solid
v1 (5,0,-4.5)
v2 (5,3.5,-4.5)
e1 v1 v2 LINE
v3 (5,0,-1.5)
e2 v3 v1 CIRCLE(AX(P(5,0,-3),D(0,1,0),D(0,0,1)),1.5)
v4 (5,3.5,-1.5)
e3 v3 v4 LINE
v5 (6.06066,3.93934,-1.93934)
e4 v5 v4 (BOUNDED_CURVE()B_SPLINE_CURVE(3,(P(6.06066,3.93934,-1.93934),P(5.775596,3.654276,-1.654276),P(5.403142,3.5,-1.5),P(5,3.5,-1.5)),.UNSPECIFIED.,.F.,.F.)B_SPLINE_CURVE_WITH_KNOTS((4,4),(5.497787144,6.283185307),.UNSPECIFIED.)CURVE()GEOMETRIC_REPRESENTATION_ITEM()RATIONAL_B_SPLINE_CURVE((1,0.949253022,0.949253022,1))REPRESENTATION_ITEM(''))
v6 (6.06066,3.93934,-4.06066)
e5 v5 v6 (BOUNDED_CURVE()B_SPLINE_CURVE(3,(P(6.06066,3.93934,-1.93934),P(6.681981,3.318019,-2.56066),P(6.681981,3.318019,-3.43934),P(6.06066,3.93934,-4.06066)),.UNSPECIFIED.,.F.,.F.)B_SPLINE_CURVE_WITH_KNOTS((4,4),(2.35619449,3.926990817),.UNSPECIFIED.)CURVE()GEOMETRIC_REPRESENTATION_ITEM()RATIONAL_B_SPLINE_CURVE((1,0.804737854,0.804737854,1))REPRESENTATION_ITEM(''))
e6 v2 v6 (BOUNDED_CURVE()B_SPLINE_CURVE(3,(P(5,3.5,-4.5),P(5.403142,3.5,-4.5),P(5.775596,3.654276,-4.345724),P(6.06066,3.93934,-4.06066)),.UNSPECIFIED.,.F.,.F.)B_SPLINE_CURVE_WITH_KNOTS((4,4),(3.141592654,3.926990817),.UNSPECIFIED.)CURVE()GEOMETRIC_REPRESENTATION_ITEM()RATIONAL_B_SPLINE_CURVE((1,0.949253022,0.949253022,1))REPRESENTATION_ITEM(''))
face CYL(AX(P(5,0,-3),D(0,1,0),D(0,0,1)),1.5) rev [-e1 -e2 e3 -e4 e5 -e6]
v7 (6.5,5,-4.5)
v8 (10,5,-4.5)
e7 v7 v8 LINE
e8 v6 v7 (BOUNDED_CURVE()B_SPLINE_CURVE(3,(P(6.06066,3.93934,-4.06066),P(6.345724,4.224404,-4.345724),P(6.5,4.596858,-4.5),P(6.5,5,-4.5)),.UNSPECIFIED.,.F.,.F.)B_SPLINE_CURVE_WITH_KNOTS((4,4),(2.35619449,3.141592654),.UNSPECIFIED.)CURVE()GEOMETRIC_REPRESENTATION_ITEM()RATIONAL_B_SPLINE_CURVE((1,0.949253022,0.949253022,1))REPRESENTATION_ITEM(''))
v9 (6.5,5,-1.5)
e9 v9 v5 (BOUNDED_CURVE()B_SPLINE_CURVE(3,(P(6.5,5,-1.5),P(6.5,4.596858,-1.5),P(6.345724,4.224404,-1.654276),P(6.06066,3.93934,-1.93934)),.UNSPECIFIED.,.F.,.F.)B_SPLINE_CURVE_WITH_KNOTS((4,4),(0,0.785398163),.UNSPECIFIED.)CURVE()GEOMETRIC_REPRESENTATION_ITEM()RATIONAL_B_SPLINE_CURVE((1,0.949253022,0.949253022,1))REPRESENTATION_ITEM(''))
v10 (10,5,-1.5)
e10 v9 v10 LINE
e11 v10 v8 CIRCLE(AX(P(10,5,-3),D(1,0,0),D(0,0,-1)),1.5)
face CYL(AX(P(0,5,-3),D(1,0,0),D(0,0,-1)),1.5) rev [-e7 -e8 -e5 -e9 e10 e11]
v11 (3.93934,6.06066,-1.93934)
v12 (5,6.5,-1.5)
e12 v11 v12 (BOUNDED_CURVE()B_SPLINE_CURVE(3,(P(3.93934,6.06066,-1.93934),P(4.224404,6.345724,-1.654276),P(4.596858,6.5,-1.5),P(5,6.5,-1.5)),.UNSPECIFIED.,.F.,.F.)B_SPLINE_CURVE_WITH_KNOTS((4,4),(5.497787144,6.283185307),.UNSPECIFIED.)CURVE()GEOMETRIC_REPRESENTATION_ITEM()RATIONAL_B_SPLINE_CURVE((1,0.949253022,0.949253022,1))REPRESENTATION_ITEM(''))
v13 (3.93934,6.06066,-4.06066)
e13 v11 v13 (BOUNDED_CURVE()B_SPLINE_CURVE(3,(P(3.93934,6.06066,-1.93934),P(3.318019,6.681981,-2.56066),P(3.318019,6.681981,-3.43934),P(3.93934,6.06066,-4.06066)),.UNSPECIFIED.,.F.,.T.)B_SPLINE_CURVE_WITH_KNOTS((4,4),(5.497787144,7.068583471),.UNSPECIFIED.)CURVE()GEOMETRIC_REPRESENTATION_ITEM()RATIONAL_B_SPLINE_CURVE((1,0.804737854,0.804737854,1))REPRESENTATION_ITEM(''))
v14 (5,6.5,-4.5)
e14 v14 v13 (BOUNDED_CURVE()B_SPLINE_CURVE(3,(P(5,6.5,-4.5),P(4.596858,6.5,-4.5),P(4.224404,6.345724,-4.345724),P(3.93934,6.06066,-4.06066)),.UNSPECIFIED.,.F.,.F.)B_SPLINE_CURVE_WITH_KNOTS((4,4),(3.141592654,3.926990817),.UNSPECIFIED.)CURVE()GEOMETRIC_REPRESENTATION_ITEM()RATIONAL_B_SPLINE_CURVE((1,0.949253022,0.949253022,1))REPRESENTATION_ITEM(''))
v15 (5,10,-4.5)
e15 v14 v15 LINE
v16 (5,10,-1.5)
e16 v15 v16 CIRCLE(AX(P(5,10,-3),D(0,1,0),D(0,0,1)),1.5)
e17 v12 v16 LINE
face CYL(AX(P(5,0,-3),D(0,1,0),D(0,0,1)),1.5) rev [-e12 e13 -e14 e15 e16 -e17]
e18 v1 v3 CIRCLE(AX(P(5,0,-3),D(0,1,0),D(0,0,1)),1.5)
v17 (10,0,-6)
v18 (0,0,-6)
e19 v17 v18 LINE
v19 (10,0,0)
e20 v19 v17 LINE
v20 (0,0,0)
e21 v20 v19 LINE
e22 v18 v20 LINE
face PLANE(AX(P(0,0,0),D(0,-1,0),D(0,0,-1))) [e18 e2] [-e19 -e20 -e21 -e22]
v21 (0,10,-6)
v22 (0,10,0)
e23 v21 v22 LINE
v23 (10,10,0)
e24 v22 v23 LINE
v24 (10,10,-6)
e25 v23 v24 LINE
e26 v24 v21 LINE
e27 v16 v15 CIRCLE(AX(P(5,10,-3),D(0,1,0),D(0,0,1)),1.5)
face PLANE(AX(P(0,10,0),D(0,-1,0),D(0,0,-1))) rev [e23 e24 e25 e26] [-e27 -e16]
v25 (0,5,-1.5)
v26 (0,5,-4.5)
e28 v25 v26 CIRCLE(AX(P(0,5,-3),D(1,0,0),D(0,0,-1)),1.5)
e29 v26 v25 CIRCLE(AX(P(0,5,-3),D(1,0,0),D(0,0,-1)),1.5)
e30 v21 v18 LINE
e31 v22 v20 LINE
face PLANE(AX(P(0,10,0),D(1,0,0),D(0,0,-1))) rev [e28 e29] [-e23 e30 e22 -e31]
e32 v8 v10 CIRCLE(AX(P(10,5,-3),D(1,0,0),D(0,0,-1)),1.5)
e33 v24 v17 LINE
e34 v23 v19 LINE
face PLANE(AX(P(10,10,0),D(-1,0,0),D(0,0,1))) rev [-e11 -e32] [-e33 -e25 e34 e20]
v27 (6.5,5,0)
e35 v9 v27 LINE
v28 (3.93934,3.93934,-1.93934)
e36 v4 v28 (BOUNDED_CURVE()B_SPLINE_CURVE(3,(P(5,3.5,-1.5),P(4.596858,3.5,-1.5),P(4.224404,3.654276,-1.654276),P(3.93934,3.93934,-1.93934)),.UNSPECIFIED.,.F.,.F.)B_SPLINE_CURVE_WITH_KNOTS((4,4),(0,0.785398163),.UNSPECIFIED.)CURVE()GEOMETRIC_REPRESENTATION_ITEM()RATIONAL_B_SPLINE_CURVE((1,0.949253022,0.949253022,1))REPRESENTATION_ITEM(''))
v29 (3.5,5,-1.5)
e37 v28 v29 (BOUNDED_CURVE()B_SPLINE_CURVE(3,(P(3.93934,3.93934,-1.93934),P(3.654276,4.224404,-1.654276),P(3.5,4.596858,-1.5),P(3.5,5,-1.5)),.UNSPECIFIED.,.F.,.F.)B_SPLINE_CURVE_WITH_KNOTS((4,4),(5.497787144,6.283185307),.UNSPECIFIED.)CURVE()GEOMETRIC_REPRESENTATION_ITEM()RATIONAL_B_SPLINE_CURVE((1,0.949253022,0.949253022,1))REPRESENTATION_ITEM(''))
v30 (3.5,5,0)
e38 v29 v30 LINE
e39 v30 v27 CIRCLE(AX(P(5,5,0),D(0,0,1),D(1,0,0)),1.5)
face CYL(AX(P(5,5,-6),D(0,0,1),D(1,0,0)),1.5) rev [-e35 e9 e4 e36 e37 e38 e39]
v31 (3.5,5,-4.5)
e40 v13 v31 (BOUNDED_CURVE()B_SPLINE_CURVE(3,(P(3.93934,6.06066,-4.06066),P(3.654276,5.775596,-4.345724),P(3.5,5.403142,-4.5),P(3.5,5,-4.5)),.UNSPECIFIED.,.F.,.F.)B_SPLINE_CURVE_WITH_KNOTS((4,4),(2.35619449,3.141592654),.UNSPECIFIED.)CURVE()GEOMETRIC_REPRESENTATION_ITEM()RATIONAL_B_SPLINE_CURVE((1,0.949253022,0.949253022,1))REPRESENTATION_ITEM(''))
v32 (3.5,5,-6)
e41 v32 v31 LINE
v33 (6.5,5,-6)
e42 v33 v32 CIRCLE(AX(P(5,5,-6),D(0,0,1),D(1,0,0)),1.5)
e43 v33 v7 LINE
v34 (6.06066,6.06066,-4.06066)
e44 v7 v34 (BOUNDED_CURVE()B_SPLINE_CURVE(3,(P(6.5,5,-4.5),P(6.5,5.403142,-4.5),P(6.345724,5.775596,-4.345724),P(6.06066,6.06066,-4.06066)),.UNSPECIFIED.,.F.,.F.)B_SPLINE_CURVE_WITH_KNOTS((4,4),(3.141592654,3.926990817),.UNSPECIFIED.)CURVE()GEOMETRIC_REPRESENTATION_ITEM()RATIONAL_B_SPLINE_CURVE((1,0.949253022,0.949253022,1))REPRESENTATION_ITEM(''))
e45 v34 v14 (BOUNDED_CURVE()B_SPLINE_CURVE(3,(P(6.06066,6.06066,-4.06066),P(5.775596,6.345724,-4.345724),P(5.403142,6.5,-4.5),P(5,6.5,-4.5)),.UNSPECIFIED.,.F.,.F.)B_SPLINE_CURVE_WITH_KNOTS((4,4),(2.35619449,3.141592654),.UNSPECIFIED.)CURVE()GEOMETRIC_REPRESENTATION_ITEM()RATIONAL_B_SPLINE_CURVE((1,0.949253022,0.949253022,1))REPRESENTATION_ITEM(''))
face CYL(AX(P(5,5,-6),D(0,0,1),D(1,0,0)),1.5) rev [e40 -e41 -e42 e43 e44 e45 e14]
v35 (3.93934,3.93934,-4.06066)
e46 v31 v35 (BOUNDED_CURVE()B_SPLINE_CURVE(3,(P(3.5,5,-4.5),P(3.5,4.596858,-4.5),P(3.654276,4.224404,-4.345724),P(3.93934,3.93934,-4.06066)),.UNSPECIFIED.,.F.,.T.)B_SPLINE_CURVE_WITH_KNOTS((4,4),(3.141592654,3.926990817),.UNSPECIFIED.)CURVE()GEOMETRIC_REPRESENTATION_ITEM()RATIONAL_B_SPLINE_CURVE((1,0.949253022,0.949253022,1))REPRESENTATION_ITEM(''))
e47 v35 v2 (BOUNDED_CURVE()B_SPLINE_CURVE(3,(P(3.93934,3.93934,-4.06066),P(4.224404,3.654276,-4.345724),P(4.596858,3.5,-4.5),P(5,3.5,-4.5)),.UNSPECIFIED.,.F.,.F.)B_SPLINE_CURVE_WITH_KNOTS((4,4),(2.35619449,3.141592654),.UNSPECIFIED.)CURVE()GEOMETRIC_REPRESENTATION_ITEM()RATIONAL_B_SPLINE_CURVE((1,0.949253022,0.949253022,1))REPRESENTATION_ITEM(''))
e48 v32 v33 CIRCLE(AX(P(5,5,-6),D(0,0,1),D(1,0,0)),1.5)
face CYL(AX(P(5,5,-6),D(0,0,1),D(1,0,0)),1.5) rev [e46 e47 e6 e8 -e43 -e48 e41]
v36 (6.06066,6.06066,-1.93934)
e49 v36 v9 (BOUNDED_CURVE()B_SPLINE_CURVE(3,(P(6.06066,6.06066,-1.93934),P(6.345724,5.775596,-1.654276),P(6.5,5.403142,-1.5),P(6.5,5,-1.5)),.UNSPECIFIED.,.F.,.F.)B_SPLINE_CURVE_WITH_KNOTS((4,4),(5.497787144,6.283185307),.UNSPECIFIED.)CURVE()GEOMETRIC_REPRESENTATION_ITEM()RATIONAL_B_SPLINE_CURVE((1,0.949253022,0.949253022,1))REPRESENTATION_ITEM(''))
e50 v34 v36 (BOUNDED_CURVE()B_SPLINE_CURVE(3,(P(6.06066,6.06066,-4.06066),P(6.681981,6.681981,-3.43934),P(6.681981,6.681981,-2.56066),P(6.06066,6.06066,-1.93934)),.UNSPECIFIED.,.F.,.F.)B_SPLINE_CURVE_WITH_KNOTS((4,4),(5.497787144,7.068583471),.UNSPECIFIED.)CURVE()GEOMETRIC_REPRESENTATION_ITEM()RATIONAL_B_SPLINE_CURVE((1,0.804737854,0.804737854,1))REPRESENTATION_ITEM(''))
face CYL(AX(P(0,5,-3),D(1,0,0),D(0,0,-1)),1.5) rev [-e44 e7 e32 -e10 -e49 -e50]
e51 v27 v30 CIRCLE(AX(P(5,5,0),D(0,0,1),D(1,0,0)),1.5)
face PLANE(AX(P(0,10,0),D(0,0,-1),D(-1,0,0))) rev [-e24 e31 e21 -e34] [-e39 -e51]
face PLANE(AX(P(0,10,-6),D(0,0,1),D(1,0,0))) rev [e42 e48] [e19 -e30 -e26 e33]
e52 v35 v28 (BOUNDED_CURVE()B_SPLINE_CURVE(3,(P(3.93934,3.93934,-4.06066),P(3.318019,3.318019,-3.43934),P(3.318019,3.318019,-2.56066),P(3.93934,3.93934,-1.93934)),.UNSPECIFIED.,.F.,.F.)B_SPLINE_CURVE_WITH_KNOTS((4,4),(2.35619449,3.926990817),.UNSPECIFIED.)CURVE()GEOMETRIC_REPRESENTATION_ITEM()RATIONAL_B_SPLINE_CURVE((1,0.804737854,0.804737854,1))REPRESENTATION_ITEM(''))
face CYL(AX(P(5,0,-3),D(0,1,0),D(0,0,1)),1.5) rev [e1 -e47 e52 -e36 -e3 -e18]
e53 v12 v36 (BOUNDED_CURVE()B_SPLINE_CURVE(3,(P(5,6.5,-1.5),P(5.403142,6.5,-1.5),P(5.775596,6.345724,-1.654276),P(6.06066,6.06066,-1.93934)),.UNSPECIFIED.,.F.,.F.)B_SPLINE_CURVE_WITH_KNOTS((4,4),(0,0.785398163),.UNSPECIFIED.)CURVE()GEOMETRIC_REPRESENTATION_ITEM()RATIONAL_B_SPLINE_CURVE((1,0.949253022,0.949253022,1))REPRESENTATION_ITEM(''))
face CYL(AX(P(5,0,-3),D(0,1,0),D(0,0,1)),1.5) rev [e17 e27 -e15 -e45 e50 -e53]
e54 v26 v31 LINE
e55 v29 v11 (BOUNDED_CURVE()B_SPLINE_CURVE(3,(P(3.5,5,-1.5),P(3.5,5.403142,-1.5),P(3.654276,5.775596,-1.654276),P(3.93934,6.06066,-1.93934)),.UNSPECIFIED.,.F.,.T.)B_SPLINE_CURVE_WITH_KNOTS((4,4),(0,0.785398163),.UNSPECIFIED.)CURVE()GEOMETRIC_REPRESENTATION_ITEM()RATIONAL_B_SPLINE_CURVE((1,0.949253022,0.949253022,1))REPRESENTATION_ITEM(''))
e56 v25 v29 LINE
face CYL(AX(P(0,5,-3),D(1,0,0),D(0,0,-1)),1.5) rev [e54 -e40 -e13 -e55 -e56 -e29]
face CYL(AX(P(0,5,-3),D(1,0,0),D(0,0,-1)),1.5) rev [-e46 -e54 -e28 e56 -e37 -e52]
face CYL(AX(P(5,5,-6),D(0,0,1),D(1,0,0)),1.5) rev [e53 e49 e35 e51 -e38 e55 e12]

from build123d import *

# Parameters (mm, degrees)
SKETCH_1_W          = 10
SKETCH_1_H          = 6
EXTRUDE_1_DEPTH     = 10
SKETCH_2_R          = 1.5
CUT_EXTRUDE_1_DEPTH = 16.362291496
SKETCH_4_R          = 1.5
CUT_EXTRUDE_2_DEPTH = 16.362291496
SKETCH_3_R          = 1.5
CUT_EXTRUDE_3_DEPTH = 16.362291496


with BuildPart() as part:
    # 草图1 → 凸台-拉伸1 (new body)
    with BuildSketch(Plane(origin=(0, 0, 0), x_dir=(1, 0, 0), z_dir=(0, 1, 0))):
        with Locations((5, 3)):
            Rectangle(SKETCH_1_W, SKETCH_1_H)
    extrude(amount=EXTRUDE_1_DEPTH)

    # 草图2 → 切除-拉伸1 (cut, through all)
    with BuildSketch(Plane.XY):
        with Locations((5, 5)):
            Circle(SKETCH_2_R)
    extrude(amount=-CUT_EXTRUDE_1_DEPTH, mode=Mode.SUBTRACT)

    # 草图4 → 切除-拉伸2 (cut, through all)
    with BuildSketch(Plane(origin=(0, 10, 0), x_dir=(1, 0, 0), z_dir=(0, 1, 0))):
        with Locations(Location((5, 3, 0), (0, 0, 270))):
            Circle(SKETCH_4_R)
    extrude(amount=-CUT_EXTRUDE_2_DEPTH, mode=Mode.SUBTRACT)

    # 草图3 → 切除-拉伸3 (cut, through all)
    with BuildSketch(Plane(origin=(10, 0, 0), x_dir=(0, 0, -1), z_dir=(1, 0, 0))):
        with Locations((3, 5)):
            Circle(SKETCH_3_R)
    extrude(amount=-CUT_EXTRUDE_3_DEPTH, mode=Mode.SUBTRACT)


solid = part.part
